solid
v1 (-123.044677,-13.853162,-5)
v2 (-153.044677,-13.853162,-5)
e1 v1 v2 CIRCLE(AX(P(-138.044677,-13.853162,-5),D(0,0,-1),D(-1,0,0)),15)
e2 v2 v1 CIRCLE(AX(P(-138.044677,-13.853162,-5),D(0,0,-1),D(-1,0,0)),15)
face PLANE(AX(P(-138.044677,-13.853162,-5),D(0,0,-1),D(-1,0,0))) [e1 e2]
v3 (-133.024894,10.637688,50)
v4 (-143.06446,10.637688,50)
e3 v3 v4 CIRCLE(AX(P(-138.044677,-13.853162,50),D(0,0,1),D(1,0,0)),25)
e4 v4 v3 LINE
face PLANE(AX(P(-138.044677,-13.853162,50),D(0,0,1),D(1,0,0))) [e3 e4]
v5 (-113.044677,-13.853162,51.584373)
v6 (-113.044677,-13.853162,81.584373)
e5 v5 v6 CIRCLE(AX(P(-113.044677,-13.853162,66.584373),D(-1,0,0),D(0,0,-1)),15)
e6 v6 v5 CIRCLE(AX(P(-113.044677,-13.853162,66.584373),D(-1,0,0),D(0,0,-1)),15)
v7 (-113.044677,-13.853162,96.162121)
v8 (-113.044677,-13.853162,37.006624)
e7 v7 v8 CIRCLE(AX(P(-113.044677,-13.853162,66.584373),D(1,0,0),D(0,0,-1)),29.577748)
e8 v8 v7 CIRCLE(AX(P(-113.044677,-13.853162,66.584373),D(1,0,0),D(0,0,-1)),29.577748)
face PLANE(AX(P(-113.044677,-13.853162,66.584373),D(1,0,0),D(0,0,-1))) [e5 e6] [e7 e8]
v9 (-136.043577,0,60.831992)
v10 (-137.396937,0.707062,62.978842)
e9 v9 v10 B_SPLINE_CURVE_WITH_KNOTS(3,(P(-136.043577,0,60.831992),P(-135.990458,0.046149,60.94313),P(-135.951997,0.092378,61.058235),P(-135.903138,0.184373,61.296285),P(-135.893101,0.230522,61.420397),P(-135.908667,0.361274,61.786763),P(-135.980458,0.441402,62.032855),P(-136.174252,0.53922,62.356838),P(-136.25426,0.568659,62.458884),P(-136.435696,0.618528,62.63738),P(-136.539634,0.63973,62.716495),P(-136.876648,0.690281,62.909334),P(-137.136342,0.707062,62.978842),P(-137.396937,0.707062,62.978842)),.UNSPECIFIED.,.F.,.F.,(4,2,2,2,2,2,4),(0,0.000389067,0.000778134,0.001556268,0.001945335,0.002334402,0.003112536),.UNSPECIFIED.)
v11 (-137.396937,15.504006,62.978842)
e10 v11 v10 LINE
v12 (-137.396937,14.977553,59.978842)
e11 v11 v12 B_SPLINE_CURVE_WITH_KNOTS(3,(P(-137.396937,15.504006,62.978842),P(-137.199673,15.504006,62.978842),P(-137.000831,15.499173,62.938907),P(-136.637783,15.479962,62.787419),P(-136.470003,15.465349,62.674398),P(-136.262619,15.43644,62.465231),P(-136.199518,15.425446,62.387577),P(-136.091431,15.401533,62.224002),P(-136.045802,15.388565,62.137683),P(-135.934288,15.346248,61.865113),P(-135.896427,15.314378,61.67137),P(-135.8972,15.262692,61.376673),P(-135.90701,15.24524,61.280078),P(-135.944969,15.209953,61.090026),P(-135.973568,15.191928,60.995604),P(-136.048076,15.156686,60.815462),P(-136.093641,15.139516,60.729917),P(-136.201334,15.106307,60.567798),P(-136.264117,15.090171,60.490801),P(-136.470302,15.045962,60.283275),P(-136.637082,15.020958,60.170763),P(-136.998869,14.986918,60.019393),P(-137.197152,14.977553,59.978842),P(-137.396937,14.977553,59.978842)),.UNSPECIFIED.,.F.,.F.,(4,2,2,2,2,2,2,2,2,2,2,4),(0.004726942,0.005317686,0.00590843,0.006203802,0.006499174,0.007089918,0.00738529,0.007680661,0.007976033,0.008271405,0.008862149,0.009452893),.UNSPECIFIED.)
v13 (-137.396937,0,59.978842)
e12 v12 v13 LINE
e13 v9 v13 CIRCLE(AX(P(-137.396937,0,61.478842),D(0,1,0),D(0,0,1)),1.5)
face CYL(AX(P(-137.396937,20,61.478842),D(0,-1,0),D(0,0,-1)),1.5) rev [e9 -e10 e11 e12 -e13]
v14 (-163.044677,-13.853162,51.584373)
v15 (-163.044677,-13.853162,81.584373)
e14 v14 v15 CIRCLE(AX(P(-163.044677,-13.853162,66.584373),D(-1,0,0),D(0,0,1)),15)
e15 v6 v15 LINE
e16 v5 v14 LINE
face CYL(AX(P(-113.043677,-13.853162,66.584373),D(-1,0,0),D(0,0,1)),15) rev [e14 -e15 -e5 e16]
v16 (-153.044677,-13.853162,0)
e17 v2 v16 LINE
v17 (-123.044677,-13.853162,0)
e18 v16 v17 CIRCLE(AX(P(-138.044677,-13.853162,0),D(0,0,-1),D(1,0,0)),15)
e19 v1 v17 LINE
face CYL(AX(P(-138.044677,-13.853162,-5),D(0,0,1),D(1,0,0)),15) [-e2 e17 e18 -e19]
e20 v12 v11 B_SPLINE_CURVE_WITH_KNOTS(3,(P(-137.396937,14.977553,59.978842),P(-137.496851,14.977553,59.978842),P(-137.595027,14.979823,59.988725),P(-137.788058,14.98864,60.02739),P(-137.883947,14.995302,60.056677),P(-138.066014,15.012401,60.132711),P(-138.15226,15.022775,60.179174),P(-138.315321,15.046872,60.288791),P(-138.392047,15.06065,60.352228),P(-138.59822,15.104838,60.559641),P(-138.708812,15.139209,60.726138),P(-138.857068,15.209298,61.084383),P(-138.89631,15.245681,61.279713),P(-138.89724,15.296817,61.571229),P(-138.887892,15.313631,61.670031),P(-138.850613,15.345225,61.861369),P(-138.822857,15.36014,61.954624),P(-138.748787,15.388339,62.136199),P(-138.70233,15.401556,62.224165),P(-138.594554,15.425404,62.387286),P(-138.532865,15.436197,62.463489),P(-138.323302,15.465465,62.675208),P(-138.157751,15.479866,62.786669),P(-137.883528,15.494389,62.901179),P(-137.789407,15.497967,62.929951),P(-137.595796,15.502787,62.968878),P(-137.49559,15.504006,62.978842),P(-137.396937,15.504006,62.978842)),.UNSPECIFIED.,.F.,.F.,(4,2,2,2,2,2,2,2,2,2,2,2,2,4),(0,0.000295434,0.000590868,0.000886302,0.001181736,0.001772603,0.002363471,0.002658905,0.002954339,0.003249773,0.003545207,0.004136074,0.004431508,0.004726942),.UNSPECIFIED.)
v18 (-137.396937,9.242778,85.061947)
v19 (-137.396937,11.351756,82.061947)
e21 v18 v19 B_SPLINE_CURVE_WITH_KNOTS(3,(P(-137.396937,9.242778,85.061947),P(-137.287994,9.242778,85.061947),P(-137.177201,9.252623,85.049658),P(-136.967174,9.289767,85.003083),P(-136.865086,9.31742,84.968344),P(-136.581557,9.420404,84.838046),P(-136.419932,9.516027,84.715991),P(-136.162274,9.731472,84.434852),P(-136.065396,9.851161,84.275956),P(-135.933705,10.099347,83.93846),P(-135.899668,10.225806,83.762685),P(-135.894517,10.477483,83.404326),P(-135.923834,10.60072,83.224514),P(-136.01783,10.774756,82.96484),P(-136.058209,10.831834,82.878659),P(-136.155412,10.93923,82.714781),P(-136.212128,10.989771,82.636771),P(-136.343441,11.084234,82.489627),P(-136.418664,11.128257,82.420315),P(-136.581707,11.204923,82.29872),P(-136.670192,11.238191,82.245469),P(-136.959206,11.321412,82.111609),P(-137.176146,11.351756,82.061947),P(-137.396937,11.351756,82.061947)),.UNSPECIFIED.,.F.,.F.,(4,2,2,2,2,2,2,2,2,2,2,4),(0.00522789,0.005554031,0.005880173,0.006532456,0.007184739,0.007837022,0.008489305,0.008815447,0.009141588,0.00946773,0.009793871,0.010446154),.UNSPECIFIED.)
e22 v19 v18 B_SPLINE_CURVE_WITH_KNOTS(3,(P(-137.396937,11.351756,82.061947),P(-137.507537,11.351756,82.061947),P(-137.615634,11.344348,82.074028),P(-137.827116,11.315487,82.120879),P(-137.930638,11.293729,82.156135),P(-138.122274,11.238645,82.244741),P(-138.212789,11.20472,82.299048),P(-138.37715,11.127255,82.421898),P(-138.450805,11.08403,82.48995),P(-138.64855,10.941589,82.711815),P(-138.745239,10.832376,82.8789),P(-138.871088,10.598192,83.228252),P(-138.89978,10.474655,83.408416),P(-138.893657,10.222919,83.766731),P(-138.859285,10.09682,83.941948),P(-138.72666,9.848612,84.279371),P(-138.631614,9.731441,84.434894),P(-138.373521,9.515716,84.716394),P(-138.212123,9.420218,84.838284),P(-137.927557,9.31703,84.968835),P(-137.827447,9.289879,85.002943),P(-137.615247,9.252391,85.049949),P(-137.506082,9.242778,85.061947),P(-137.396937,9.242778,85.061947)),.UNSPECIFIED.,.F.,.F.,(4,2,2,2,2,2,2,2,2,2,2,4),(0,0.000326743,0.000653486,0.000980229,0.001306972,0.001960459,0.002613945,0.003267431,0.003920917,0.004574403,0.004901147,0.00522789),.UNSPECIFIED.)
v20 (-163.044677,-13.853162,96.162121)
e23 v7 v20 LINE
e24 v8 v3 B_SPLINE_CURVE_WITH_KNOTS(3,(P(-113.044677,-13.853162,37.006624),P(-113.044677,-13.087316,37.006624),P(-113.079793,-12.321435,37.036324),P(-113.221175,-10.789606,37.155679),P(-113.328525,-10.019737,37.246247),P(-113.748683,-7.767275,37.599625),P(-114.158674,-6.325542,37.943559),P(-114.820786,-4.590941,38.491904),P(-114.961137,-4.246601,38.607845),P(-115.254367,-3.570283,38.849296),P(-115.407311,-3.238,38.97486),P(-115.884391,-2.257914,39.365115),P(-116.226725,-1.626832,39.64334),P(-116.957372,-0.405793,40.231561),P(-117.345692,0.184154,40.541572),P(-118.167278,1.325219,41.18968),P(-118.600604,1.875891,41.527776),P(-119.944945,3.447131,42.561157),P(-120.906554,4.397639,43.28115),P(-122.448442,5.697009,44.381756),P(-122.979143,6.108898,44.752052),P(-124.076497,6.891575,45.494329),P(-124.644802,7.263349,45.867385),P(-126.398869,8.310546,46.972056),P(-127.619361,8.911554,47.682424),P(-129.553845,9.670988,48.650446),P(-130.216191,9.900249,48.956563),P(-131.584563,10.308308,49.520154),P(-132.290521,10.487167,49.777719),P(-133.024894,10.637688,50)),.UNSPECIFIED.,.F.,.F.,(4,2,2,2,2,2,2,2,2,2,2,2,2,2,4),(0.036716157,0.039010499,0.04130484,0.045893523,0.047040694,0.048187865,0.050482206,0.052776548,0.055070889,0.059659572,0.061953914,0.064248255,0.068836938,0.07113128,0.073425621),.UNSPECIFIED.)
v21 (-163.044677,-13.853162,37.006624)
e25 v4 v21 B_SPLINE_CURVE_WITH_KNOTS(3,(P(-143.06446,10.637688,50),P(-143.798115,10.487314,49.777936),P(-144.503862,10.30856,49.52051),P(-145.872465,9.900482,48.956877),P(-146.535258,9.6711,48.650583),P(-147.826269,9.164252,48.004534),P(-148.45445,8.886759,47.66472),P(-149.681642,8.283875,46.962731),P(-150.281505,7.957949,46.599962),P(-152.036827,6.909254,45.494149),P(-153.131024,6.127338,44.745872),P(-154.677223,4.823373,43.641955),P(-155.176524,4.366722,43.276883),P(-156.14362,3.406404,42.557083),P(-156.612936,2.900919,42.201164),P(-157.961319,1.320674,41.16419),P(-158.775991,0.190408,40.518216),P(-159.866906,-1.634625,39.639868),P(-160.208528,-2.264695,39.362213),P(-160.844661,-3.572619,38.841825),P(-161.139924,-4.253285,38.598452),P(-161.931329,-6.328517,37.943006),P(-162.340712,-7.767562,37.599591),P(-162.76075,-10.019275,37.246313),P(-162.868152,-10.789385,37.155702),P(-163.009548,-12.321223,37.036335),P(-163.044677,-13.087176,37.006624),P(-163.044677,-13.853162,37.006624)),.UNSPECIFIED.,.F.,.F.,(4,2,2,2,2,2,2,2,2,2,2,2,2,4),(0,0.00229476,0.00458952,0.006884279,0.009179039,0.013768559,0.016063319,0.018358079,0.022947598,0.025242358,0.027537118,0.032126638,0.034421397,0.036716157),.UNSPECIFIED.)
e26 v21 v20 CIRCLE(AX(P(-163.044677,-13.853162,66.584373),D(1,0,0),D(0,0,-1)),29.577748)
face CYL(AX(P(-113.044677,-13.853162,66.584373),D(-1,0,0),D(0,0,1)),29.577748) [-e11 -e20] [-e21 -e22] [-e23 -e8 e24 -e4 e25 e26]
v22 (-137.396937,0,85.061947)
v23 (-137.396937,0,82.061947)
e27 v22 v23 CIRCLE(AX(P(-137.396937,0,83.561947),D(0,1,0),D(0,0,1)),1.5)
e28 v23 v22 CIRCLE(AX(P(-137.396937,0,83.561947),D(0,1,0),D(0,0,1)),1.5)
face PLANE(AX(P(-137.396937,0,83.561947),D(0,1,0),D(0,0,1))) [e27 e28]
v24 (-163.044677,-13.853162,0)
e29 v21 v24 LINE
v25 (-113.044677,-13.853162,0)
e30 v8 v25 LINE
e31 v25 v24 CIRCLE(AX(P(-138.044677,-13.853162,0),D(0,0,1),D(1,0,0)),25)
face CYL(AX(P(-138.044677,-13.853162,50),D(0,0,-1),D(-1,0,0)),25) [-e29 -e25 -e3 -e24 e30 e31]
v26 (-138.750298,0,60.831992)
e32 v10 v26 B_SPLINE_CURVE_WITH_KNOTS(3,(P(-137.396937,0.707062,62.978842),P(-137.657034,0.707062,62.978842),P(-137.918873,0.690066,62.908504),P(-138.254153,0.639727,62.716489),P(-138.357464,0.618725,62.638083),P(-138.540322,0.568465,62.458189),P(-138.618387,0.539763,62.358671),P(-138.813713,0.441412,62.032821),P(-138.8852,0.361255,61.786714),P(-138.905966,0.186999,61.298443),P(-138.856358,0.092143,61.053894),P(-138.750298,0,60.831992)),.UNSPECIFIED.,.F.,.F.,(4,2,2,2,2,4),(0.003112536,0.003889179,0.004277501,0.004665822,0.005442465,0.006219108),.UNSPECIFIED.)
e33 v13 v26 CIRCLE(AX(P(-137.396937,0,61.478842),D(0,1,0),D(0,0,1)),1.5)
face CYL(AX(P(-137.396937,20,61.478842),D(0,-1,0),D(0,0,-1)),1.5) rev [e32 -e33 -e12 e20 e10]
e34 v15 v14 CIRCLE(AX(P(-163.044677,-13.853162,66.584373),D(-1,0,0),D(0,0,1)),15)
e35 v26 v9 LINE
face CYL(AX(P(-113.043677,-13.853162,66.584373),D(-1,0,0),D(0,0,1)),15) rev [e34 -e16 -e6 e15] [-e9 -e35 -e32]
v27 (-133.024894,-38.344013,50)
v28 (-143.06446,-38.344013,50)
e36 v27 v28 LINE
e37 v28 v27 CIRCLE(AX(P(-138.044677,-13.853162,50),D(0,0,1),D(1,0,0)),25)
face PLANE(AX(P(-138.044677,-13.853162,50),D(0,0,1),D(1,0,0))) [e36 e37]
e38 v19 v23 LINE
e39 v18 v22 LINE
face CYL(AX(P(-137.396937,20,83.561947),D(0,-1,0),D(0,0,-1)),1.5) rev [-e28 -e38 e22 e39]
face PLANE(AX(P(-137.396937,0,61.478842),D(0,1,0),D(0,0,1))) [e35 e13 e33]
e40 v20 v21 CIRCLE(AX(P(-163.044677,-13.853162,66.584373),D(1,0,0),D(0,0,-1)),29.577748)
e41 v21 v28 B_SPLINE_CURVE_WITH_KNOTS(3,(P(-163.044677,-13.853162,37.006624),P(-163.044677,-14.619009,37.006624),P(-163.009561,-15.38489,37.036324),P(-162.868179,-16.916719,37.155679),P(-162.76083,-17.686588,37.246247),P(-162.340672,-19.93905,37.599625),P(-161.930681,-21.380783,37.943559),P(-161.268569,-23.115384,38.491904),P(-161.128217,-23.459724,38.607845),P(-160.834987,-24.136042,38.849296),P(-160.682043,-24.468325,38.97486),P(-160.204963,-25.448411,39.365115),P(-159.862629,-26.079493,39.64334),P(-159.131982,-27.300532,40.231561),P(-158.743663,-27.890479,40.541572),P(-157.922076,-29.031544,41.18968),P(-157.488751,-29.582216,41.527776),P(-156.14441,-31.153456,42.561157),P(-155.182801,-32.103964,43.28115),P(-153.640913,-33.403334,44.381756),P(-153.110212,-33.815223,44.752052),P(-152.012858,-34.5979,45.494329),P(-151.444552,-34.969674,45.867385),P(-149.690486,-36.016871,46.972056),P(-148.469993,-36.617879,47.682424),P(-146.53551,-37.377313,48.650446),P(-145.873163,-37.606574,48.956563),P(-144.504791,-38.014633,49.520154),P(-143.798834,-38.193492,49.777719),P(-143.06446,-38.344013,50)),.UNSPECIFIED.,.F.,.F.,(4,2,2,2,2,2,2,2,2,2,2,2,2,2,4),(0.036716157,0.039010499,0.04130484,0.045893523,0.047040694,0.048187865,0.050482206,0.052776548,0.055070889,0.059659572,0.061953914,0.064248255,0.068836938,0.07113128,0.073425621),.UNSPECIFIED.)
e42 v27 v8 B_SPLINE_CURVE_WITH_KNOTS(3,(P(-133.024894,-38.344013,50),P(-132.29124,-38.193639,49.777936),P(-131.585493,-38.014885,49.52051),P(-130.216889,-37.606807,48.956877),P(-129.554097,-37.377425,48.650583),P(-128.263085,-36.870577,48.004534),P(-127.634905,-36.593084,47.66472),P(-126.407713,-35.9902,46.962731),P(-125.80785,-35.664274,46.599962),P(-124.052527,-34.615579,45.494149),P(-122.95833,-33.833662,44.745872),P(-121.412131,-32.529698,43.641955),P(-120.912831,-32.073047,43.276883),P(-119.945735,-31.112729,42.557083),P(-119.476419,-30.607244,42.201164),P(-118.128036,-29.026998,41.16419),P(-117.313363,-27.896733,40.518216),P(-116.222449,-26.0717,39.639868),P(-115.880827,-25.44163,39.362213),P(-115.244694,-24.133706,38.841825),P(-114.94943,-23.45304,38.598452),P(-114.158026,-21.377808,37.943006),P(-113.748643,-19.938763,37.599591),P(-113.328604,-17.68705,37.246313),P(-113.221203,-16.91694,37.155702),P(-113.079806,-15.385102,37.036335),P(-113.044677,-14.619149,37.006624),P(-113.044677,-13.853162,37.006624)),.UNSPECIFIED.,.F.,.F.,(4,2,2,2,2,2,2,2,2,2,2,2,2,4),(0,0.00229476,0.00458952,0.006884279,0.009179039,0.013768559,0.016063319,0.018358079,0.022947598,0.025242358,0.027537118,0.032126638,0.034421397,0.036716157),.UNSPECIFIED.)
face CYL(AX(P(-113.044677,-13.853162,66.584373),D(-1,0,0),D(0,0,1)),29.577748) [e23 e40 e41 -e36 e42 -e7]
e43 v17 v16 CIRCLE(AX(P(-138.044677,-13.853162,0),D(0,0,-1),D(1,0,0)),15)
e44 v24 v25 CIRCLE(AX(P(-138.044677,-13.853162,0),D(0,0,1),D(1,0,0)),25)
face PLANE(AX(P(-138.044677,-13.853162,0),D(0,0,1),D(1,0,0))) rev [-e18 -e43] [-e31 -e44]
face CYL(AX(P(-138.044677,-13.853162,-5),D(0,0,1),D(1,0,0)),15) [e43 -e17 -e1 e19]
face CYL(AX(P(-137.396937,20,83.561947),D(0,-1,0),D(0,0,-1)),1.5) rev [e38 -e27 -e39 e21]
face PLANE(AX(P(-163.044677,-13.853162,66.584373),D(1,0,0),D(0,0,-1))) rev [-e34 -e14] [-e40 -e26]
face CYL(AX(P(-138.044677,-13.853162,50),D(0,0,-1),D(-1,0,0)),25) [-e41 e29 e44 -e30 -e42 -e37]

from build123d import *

# Parameters (mm, degrees)
SKETCH1_R           = 25
BOSS_EXTRUDE1_DEPTH = 50
SKETCH3_R           = 29.577748383
BOSS_EXTRUDE2_DEPTH = 25
SKETCH4_R           = 15
BOSS_EXTRUDE3_DEPTH = 5
CUT_EXTRUDE1_REACH  = 118.762
SKETCH5_R           = 15
SKETCH6_R           = 1.5
CUT_EXTRUDE2_DEPTH  = 20


with BuildPart() as part:
    # Sketch1 → Boss-Extrude1 (new body)
    with BuildSketch(Plane.XY):
        with Locations((-138.044677266, -13.853162466)):
            Circle(SKETCH1_R)
    extrude(amount=BOSS_EXTRUDE1_DEPTH)

    # Sketch3 → Boss-Extrude2 (add, symmetric)
    with BuildSketch(Plane(origin=(-138.044677266, 0, 0), x_dir=(0, 0, -1), z_dir=(1, 0, 0))):
        with Locations((-66.584372838, -13.853162466)):
            Circle(SKETCH3_R)
    extrude(amount=BOSS_EXTRUDE2_DEPTH, both=True)

    # Sketch4 → Boss-Extrude3 (add, symmetric)
    with BuildSketch(Plane(origin=(0, 0, 0), x_dir=(-1, 0, 0), z_dir=(0, 0, -1))):
        with Locations(Location((138.044677266, -13.853162466, 0), (0, 0, 180))):
            Circle(SKETCH4_R)
    extrude(amount=BOSS_EXTRUDE3_DEPTH, both=True)

    # Sketch5 → Cut-Extrude1 (cut, up to next)
    with BuildSketch(Plane.ZY.offset(163.044677266), mode=Mode.PRIVATE) as cut_extrude1_sk1:
        with Locations((66.584372838, -13.853162466)):
            Circle(SKETCH5_R)
    cut_extrude1_tool1 = extrude(cut_extrude1_sk1.sketch, amount=-CUT_EXTRUDE1_REACH, mode=Mode.PRIVATE) & part.part
    add(cut_extrude1_tool1.solids().sort_by_distance((-163.044677, -13.853162, 66.584373))[0], mode=Mode.SUBTRACT)

    # Sketch6 → Cut-Extrude2 (cut)
    with BuildSketch(Plane(origin=(0, 0, 0), x_dir=(1, 0, 0), z_dir=(0, 1, 0))):
        with Locations(Location((-137.396937397, -61.478842375, 0), (0, 0, 90))):
            Circle(SKETCH6_R)
        with Locations(Location((-137.396937397, -83.561946624, 0), (0, 0, 90))):
            Circle(SKETCH6_R)
    extrude(amount=CUT_EXTRUDE2_DEPTH, mode=Mode.SUBTRACT)


solid = part.part
